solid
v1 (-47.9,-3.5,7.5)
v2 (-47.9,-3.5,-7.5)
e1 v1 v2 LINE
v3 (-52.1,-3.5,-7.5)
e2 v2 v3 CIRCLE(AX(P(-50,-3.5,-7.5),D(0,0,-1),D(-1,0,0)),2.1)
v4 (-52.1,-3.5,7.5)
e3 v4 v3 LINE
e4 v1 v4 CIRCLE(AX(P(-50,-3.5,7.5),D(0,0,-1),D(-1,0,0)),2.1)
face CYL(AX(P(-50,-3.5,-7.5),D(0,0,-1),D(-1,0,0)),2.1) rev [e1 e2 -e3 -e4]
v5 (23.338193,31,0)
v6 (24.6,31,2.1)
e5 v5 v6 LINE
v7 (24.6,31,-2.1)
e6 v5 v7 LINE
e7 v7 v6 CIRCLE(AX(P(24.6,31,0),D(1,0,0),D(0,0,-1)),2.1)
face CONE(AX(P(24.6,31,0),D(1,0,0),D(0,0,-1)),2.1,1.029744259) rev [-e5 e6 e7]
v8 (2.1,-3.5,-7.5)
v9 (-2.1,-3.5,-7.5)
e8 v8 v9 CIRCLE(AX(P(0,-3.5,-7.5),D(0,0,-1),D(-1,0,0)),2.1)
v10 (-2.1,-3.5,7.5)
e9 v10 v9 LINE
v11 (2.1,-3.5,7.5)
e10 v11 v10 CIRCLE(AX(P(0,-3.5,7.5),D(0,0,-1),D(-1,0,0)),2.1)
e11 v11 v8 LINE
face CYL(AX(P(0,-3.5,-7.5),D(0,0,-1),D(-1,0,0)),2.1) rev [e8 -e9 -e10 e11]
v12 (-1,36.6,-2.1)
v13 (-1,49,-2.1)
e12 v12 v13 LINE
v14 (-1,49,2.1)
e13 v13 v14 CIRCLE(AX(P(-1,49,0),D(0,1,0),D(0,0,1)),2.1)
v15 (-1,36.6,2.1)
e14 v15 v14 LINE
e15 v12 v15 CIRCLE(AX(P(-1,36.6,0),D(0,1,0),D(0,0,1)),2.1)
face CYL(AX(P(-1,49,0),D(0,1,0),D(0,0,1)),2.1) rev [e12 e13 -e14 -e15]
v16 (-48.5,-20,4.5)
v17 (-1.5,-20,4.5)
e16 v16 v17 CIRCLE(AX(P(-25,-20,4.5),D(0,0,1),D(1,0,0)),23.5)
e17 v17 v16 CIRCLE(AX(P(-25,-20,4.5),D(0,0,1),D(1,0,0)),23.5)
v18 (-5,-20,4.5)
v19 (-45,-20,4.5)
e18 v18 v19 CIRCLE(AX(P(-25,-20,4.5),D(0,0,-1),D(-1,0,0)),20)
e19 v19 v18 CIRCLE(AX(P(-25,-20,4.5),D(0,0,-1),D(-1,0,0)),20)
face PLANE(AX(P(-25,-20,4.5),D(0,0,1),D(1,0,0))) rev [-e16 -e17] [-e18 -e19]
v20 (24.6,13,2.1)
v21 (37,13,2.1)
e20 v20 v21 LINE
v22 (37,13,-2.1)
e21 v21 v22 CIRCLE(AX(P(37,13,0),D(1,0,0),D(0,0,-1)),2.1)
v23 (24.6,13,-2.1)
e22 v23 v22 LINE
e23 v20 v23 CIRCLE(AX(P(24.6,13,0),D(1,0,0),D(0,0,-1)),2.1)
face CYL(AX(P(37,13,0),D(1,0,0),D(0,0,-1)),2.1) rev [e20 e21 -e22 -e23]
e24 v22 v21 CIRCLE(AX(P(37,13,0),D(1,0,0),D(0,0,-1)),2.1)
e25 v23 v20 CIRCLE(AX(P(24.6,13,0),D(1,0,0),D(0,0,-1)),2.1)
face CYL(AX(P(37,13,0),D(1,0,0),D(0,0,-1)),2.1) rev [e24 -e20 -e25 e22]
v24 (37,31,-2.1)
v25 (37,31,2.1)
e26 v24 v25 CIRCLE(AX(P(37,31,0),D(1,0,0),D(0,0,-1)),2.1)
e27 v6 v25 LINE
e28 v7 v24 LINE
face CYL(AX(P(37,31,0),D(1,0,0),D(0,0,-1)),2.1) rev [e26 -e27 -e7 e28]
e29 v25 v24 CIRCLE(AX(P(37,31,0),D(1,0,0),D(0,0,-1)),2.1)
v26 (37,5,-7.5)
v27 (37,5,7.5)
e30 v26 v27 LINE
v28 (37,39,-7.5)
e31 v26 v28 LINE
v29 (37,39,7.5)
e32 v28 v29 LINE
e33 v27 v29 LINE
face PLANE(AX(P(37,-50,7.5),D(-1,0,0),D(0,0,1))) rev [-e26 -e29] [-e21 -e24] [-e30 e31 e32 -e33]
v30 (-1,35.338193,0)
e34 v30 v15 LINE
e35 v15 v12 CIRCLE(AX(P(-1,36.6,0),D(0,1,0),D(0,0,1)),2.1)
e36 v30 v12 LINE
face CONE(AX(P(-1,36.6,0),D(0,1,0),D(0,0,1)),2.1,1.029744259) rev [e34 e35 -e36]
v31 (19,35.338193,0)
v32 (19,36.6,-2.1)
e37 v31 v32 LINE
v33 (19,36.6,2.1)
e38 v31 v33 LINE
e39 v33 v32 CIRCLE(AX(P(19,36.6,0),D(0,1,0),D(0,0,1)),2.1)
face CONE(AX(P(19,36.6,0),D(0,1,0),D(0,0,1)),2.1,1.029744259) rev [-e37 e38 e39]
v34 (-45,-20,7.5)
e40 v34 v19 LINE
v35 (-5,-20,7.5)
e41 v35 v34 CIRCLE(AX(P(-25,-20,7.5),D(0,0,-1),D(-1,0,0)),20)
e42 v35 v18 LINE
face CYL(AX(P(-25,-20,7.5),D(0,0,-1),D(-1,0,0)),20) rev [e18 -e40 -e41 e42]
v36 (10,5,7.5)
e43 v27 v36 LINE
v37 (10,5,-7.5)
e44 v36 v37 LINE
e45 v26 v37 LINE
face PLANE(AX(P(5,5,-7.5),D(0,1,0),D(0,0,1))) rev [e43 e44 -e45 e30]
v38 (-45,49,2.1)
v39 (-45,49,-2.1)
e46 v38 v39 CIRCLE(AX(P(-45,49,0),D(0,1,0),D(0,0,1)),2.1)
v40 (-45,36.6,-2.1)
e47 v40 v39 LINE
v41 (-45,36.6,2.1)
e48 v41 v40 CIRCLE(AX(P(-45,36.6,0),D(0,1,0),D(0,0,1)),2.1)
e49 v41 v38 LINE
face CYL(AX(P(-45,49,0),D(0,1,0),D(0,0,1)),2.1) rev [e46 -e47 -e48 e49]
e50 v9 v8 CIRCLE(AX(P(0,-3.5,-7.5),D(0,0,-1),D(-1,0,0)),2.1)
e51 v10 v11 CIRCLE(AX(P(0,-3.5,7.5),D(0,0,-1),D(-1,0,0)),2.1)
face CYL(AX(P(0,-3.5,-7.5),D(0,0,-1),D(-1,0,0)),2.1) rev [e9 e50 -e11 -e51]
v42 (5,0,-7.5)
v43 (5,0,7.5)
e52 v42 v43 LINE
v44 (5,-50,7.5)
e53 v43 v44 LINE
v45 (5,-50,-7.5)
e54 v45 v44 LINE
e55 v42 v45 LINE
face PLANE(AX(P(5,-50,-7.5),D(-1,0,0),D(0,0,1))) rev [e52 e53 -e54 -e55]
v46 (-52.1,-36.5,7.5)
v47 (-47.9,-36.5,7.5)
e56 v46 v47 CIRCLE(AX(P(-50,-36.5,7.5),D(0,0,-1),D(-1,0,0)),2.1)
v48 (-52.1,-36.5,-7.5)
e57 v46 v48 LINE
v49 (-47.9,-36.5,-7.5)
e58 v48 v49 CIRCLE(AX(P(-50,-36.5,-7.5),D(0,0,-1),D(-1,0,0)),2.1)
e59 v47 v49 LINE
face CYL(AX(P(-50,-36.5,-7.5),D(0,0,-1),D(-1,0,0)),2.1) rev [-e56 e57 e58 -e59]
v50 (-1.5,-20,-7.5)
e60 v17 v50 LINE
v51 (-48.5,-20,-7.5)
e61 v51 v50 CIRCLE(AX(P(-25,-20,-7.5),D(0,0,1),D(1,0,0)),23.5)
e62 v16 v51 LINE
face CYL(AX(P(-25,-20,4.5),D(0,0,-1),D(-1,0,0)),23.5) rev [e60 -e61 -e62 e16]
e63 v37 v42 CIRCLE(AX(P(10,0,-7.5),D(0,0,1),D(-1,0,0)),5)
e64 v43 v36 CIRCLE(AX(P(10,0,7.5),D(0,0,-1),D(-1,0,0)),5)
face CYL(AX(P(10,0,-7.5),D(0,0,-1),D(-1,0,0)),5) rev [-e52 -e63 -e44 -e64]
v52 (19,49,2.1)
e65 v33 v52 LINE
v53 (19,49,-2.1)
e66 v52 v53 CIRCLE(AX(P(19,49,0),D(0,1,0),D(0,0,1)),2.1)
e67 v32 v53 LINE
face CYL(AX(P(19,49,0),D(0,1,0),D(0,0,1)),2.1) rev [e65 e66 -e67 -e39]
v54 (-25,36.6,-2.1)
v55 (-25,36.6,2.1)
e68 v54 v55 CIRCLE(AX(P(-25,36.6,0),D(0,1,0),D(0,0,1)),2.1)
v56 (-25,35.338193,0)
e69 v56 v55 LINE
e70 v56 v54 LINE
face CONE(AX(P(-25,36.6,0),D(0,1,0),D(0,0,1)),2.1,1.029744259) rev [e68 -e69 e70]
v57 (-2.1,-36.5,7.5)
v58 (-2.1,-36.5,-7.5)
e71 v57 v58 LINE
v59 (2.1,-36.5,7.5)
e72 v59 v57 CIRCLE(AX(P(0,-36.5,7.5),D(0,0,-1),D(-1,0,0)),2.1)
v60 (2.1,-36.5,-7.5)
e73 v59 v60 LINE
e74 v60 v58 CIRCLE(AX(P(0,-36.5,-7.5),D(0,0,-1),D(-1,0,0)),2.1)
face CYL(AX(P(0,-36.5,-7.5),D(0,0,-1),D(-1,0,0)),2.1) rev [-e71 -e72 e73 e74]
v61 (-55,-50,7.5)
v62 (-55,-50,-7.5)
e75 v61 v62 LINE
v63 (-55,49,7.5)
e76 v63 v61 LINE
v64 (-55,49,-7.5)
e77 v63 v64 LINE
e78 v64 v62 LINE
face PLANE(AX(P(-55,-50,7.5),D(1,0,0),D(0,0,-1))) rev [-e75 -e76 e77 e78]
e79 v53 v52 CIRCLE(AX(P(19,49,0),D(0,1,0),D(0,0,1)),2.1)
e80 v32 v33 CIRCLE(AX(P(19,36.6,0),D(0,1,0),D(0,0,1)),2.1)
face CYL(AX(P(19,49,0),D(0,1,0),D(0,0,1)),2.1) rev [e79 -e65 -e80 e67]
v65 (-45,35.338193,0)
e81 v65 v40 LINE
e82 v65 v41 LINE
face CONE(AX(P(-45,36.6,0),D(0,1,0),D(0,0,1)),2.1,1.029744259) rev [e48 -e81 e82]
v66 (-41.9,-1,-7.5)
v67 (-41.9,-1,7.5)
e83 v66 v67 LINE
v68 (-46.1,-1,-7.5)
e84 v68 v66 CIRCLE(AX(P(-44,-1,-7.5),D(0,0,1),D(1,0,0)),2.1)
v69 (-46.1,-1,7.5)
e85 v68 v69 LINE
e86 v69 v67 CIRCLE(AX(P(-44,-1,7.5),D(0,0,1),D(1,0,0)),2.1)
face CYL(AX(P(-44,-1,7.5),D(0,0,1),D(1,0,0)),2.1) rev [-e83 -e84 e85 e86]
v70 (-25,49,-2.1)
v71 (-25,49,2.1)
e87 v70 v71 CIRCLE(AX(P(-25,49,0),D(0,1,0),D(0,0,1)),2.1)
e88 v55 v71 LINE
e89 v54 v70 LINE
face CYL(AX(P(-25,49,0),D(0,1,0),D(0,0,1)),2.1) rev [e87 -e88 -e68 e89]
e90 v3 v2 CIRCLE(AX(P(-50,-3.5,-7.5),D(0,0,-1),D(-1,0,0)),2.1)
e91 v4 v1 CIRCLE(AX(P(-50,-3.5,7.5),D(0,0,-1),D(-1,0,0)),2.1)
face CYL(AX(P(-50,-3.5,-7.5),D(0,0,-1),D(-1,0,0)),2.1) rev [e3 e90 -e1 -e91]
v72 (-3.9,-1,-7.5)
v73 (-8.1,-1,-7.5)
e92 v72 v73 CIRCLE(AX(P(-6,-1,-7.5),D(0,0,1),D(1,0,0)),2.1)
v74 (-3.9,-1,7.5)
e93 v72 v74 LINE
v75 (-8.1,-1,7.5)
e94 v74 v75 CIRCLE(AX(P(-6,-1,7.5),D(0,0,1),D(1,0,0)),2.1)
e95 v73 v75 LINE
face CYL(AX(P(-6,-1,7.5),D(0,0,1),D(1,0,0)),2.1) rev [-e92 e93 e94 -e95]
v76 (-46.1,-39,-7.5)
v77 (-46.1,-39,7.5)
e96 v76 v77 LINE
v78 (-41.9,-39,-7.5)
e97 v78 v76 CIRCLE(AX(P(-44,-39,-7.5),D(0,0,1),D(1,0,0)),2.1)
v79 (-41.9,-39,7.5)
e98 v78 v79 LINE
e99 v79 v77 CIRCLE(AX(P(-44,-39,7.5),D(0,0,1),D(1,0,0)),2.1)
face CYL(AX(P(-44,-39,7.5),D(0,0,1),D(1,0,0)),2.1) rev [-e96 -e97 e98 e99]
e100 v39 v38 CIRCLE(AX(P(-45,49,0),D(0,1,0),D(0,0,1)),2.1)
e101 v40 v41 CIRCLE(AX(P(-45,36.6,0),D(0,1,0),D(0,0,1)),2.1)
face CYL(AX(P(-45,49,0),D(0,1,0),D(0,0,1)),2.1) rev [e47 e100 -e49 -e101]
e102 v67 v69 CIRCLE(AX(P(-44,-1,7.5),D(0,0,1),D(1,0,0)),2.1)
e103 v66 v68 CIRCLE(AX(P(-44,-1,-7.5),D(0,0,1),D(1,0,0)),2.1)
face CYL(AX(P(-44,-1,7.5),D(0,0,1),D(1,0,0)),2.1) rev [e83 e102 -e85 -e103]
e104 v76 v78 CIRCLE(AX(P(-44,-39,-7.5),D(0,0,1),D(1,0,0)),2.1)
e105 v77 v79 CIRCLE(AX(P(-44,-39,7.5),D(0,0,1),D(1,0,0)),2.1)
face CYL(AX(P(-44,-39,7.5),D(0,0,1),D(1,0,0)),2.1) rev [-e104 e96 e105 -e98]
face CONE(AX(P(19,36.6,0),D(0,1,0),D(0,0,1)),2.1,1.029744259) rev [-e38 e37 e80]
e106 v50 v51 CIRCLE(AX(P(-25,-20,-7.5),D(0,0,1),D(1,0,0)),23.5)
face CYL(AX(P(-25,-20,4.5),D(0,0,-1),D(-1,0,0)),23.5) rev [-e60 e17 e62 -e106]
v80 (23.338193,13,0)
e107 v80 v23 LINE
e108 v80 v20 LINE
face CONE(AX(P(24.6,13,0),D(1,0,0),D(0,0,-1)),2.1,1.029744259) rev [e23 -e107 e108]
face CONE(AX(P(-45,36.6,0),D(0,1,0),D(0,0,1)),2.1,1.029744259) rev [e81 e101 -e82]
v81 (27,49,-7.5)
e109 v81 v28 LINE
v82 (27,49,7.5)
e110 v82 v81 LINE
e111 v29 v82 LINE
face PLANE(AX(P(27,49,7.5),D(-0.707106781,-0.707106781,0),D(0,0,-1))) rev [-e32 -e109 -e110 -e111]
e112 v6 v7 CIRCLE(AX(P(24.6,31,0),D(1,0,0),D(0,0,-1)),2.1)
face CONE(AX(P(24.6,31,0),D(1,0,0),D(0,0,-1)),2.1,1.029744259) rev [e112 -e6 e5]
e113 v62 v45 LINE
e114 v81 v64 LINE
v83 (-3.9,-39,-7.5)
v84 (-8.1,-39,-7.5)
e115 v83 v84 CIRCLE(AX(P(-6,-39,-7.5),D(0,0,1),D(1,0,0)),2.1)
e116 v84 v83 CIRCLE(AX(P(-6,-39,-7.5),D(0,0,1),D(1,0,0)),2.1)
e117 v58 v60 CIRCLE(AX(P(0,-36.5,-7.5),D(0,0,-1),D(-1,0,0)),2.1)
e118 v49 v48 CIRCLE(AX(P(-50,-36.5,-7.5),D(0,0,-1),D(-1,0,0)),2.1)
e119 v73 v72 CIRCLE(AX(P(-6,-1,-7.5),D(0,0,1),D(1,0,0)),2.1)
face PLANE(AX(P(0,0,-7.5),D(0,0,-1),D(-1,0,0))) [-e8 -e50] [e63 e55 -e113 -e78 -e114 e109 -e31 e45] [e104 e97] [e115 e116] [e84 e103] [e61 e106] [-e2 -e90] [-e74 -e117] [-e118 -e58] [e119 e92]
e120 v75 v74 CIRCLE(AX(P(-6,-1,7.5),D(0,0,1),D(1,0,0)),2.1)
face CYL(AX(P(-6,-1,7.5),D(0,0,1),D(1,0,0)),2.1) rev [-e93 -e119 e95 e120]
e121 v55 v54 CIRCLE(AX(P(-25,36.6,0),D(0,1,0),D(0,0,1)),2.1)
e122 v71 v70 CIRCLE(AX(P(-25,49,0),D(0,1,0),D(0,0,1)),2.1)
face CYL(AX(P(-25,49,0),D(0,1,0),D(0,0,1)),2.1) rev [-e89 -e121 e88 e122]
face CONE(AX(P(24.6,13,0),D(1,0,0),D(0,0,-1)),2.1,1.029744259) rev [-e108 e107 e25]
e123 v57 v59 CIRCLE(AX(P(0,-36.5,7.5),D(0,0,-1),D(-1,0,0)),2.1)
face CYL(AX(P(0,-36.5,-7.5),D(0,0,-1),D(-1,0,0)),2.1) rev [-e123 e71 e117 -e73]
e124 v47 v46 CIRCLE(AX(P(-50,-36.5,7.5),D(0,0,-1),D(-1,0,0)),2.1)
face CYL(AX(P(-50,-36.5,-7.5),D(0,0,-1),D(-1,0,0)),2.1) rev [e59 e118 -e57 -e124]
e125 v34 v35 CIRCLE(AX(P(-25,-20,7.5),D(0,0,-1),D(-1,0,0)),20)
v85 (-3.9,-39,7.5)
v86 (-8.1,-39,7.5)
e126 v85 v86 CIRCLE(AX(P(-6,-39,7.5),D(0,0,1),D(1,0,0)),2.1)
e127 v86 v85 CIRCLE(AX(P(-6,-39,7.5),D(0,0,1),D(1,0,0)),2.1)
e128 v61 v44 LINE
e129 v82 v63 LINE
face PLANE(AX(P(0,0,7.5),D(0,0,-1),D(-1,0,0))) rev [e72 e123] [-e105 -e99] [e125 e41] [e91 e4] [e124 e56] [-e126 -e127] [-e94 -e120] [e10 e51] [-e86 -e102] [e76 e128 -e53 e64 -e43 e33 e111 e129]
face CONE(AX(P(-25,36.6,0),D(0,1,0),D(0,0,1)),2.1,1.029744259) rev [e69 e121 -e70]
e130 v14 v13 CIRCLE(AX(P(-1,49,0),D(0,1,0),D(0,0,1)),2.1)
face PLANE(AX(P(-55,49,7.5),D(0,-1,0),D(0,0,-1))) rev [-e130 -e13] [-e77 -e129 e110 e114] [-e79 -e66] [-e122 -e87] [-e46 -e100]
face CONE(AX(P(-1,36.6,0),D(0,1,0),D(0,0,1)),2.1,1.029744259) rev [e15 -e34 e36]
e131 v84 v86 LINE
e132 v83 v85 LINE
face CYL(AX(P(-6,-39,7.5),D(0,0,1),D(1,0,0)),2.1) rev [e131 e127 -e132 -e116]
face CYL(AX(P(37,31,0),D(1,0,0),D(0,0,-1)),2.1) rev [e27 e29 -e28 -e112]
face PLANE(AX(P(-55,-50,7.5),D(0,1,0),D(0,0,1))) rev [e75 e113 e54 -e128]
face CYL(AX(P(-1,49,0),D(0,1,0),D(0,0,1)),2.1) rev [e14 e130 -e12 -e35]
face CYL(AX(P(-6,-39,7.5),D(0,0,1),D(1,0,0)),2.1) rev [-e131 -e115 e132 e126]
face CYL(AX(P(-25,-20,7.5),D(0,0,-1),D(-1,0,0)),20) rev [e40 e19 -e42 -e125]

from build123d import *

# Parameters (mm, degrees)
SKETCH_1_W             = 110
SKETCH_1_H             = 100
EXTRUDE_1_DEPTH        = 7.5
SKETCH_10_R            = 23.5
CUT_EXTRUDE_1_DEPTH    = 12
SKETCH_12_R            = 20
CUT_EXTRUDE_2_DEPTH    = 76.292761936
SKETCH_13_W            = 50
SKETCH_13_H            = 55
CUT_EXTRUDE_3_DEPTH    = 76.828754441
FILLET_1_R             = 5
HOLE_WIZARD_M5_1_D     = 4.2
HOLE_WIZARD_M5_2_D     = 4.2
MOVE_FACE_1_BY         = 1
MOVE_FACE_2_BY         = 18
HOLE_WIZARD_M5_3_D     = 4.2
HOLE_WIZARD_M5_3_DEPTH = 12.4
HOLE_WIZARD_M5_3_TIP   = 1.2618073
HOLE_WIZARD_M5_4_D     = 4.2
HOLE_WIZARD_M5_4_DEPTH = 12.4
HOLE_WIZARD_M5_4_TIP   = 1.2618073
CHAMFER_2_SIZE         = 10


with BuildPart() as part:
    # 草图1 → 凸台-拉伸1 (new, symmetric)
    with BuildSketch(Plane.XY):
        Rectangle(SKETCH_1_W, SKETCH_1_H)
    extrude(amount=EXTRUDE_1_DEPTH, both=True)

    # 草图10 → 切除-拉伸1 (cut)
    with BuildSketch(Plane.XY.offset(-7.5)):
        with Locations((-25, -20)):
            Circle(SKETCH_10_R)
    extrude(amount=CUT_EXTRUDE_1_DEPTH, mode=Mode.SUBTRACT)

    # 草图12 → 切除-拉伸2 (cut, through all)
    with BuildSketch(Plane(origin=(0, 0, 4.5), x_dir=(-1, 0, 0), z_dir=(0, 0, -1))):
        with Locations((25, -20)):
            Circle(SKETCH_12_R)
    extrude(amount=-CUT_EXTRUDE_2_DEPTH, mode=Mode.SUBTRACT)

    # 草图13 → 切除-拉伸3 (cut, through all)
    with BuildSketch(Plane.XY.offset(7.5)):
        with Locations((30, -22.5)):
            Rectangle(SKETCH_13_W, SKETCH_13_H)
    extrude(amount=-CUT_EXTRUDE_3_DEPTH, mode=Mode.SUBTRACT)

    # 圆角1
    fillet_1_edges = [part.edges().sort_by_distance(p)[0] for p in [
        (5, 5, 0),
    ]]
    fillet(fillet_1_edges, radius=FILLET_1_R)

    # M5 螺纹孔1 (through all)
    with Locations(Plane(origin=(0, 0, -7.5), x_dir=(-1, 0, 0), z_dir=(0, 0, -1))):
        with Locations((0, -3.5), (0, -36.5), (50, -36.5), (50, -3.5)):
            Hole(HOLE_WIZARD_M5_1_D / 2)

    # M5 螺纹孔2 (through all)
    with Locations(Plane.XY.offset(7.5)):
        with Locations((-44, -1), (-44, -39), (-6, -39), (-6, -1)):
            Hole(HOLE_WIZARD_M5_2_D / 2)

    # Move Face 1: a face moved inward by 1.0
    extrude(part.faces().sort_by_distance((0, 50, 0))[0], amount=MOVE_FACE_1_BY, dir=(0, -1, 0), mode=Mode.SUBTRACT)

    # Move Face 2: a face moved inward by 18.0
    extrude(part.faces().sort_by_distance((55, 27, 0))[0], amount=MOVE_FACE_2_BY, dir=(-1, 0, 0), mode=Mode.SUBTRACT)

    # M5 螺纹孔3
    with Locations(Plane(origin=(0, 49, 0), x_dir=(1, 0, 0), z_dir=(0, 1, 0))):
        with Locations((19, 0), (-1, 0), (-25, 0), (-45, 0)):
            Hole(HOLE_WIZARD_M5_3_D / 2, depth=HOLE_WIZARD_M5_3_DEPTH)
            with Locations((0, 0, -(HOLE_WIZARD_M5_3_DEPTH + HOLE_WIZARD_M5_3_TIP / 2))):  # 118° drill point
                Cone(0, HOLE_WIZARD_M5_3_D / 2, HOLE_WIZARD_M5_3_TIP, mode=Mode.SUBTRACT)

    # M5 螺纹孔4
    with Locations(Plane(origin=(37, 0, 0), x_dir=(0, 0, -1), z_dir=(1, 0, 0))):
        with Locations((0, 13), (0, 31)):
            Hole(HOLE_WIZARD_M5_4_D / 2, depth=HOLE_WIZARD_M5_4_DEPTH)
            with Locations((0, 0, -(HOLE_WIZARD_M5_4_DEPTH + HOLE_WIZARD_M5_4_TIP / 2))):  # 118° drill point
                Cone(0, HOLE_WIZARD_M5_4_D / 2, HOLE_WIZARD_M5_4_TIP, mode=Mode.SUBTRACT)

    # 倒角2
    chamfer_2_edges = [part.edges().sort_by_distance(p)[0] for p in [
        (37, 49, 0),
    ]]
    chamfer(chamfer_2_edges, length=CHAMFER_2_SIZE)


solid = part.part
